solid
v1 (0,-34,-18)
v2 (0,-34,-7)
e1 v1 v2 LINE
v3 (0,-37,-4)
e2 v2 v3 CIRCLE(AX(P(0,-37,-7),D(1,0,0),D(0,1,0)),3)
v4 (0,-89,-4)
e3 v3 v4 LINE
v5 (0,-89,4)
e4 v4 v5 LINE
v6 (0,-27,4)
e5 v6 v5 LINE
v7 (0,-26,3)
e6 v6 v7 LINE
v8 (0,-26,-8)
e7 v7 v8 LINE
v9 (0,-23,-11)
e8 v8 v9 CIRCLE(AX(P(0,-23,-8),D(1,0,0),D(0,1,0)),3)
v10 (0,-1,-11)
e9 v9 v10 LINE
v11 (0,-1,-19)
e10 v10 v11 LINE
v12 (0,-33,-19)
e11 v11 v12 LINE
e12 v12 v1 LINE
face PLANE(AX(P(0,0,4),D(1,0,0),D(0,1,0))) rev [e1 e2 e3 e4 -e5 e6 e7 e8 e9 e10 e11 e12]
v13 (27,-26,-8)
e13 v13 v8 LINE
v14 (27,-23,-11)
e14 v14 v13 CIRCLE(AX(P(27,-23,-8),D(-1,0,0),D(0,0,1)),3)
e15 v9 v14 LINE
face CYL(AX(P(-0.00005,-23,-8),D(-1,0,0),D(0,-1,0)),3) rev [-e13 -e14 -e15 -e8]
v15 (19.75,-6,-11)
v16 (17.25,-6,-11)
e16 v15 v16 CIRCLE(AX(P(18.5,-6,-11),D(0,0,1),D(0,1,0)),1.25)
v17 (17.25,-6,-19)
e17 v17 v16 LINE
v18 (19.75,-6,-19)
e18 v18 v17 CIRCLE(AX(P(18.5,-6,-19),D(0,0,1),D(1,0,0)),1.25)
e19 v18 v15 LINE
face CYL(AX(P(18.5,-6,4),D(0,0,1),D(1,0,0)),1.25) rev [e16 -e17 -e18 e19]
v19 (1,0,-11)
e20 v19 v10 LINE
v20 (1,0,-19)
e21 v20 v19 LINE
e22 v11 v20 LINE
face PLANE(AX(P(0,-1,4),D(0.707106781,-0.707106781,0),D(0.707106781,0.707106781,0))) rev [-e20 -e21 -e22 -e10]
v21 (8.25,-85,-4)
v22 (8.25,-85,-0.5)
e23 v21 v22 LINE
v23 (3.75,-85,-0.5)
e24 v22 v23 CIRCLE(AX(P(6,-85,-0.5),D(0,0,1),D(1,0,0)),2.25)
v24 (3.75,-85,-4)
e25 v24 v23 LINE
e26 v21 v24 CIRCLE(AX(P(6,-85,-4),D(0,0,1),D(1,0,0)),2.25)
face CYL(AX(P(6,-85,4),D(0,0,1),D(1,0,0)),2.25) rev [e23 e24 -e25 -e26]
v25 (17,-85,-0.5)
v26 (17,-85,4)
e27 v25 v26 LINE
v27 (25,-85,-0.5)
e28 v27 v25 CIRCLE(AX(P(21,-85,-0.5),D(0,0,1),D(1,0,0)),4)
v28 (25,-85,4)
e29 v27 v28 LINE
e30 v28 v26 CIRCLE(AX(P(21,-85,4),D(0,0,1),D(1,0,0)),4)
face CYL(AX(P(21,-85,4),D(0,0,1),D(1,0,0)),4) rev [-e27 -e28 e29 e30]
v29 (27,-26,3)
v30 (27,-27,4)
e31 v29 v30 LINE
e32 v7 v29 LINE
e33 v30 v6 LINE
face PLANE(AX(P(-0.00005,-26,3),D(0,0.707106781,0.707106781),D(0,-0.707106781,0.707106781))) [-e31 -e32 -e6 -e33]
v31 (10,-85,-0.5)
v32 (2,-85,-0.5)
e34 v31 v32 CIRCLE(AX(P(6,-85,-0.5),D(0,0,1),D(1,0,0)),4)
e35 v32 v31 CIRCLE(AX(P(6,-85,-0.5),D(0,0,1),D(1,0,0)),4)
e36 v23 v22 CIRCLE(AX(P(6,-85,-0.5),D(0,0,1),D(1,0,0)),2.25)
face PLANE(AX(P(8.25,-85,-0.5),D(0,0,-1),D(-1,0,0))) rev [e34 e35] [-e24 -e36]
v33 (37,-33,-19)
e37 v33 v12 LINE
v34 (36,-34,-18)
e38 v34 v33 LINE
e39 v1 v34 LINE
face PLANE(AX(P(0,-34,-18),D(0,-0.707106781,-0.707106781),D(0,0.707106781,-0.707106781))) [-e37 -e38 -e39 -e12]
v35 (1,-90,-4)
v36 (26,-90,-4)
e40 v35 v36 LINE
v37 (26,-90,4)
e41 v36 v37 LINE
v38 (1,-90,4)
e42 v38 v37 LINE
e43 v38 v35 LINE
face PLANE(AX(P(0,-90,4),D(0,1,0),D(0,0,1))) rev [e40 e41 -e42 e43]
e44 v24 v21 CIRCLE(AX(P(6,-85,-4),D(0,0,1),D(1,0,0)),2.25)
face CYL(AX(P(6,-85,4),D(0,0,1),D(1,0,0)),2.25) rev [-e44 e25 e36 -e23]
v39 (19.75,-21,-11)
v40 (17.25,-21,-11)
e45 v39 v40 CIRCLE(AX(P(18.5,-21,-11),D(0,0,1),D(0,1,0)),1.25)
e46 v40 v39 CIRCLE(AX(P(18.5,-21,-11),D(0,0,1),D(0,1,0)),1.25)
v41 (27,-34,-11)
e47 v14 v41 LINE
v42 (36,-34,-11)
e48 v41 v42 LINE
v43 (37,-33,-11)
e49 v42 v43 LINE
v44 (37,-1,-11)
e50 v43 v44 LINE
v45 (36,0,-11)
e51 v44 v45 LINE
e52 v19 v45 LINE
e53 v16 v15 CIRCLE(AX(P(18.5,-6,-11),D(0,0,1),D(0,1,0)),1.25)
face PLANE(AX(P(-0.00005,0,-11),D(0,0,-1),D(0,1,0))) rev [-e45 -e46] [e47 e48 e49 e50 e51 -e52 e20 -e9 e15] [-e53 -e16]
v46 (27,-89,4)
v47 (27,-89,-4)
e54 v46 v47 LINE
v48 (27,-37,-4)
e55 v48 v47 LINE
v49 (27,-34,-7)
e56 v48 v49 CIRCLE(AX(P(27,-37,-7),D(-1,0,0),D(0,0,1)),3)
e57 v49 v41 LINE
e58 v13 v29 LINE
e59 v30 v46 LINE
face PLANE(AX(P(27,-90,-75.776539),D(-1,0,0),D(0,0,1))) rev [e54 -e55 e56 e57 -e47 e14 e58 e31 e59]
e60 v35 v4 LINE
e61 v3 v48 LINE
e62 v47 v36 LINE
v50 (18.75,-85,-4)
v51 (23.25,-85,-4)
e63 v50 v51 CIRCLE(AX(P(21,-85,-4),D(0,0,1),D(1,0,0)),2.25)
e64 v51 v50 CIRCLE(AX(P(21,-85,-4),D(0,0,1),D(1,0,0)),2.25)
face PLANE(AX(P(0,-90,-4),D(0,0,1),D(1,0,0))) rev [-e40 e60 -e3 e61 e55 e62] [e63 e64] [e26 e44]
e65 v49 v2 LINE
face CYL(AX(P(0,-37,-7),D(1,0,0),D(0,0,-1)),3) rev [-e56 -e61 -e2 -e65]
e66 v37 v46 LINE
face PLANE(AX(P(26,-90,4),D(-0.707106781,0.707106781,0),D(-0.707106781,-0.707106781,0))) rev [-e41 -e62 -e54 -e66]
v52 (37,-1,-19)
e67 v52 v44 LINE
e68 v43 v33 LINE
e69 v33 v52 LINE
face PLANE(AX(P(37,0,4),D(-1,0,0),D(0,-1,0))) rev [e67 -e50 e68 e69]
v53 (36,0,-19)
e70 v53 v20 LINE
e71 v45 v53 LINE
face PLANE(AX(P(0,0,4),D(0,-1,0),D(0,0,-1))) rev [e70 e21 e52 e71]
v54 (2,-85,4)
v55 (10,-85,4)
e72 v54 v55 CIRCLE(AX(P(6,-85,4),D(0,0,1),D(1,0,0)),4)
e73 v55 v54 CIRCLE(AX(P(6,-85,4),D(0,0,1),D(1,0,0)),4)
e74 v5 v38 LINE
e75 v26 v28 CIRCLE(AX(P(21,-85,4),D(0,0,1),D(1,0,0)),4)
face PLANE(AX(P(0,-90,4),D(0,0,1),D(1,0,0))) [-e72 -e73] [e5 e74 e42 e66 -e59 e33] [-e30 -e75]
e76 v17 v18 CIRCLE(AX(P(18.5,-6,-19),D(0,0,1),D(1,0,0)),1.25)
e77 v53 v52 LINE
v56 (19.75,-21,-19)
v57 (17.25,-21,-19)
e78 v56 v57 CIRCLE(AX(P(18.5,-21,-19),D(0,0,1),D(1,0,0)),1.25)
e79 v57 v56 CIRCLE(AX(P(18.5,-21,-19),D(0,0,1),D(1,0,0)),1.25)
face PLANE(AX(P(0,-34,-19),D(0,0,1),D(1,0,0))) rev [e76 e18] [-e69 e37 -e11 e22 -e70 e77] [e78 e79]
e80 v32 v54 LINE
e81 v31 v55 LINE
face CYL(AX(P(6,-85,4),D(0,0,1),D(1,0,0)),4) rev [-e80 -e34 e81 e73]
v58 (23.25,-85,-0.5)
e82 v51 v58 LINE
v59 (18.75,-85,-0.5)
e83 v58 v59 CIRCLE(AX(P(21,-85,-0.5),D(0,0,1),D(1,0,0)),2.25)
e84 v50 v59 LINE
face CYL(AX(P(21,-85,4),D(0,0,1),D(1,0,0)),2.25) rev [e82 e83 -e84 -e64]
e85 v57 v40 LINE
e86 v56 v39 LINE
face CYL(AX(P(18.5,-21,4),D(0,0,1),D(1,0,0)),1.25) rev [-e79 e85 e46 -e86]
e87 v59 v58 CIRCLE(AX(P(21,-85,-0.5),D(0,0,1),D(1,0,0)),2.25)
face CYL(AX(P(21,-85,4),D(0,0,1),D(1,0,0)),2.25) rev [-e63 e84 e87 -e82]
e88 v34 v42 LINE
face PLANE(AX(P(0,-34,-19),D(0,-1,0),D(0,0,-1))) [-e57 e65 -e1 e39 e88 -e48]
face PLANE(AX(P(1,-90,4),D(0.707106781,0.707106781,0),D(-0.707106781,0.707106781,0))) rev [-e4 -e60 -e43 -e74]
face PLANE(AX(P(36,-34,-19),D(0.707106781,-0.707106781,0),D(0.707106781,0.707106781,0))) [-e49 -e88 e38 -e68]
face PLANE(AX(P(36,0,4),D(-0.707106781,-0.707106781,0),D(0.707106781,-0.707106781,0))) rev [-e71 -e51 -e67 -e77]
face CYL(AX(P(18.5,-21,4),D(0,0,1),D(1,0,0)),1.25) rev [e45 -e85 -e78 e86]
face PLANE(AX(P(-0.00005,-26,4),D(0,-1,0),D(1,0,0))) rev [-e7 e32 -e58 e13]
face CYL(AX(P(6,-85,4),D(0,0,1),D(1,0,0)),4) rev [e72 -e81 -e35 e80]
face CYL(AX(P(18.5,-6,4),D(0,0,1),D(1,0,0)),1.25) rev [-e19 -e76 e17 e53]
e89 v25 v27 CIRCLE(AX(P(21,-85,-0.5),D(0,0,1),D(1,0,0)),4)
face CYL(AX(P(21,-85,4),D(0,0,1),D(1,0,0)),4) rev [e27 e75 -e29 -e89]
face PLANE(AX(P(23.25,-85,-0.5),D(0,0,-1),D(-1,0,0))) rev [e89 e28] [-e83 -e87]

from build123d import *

# Parameters (mm, degrees)
SKETCH1_W                               = 37
SKETCH1_H                               = 90
BOSS_EXTRUDE1_DEPTH                     = 4
SKETCH6_W                               = 37
SKETCH6_H                               = 34
BOSS_EXTRUDE2_DEPTH                     = 15
M3_TAPPED_HOLE1_D                       = 2.5
CBORE_FOR_M4_HEX_HEAD_BOLT1_D           = 4.5
CBORE_FOR_M4_HEX_HEAD_BOLT1_CBORE_D     = 8
CBORE_FOR_M4_HEX_HEAD_BOLT1_CBORE_DEPTH = 4.5
SKETCH7_W                               = 15
SKETCH7_H                               = 26
CUT_EXTRUDE1_DEPTH                      = 100.146356464
CUT_EXTRUDE2_REACH                      = 101.99
SKETCH8_W                               = 10
SKETCH8_H                               = 64
FILLET1_R                               = 3
CHAMFER1_SIZE                           = 1
CHAMFER2_SIZE                           = 1


with BuildPart() as part:
    # Sketch1 → Boss-Extrude1 (new, symmetric)
    with BuildSketch(Plane.XY):
        with Locations((18.5, -45)):
            Rectangle(SKETCH1_W, SKETCH1_H)
    extrude(amount=BOSS_EXTRUDE1_DEPTH, both=True)

    # Sketch6 → Boss-Extrude2 (add)
    with BuildSketch(Plane.XY.offset(-4)):
        with Locations((18.5, -17)):
            Rectangle(SKETCH6_W, SKETCH6_H)
    extrude(amount=-BOSS_EXTRUDE2_DEPTH)

    # M3 Tapped Hole1 (through all)
    with Locations(Plane.XY.offset(4)):
        with Locations((18.5, -21), (18.5, -6)):
            Hole(M3_TAPPED_HOLE1_D / 2)

    # CBORE for M4 Hex Head Bolt1 (through all)
    with Locations(Plane.XY.offset(4)):
        with Locations((6, -85), (21, -85)):
            CounterBoreHole(CBORE_FOR_M4_HEX_HEAD_BOLT1_D / 2, CBORE_FOR_M4_HEX_HEAD_BOLT1_CBORE_D / 2, CBORE_FOR_M4_HEX_HEAD_BOLT1_CBORE_DEPTH)

    # Sketch7 → Cut-Extrude1 (cut, through all)
    with BuildSketch(Plane(origin=(37, 0, 0), x_dir=(0, 0, -1), z_dir=(1, 0, 0))):
        with Locations((3.5, -13)):
            Rectangle(SKETCH7_W, SKETCH7_H)
    extrude(amount=-CUT_EXTRUDE1_DEPTH, mode=Mode.SUBTRACT)

    # Cut-Extrude2: up to this face of the body (flat: up to its plane)
    cut_extrude2_end = Plane(part.part.faces().sort_by_distance((18.5, -12.99484475, -11))[0])
    # Sketch8 → Cut-Extrude2 (cut, up to the picked face)
    with BuildSketch(Plane.XY.offset(4), mode=Mode.PRIVATE) as cut_extrude2_sk1:
        with Locations((32, -58)):
            Rectangle(SKETCH8_W, SKETCH8_H)
    cut_extrude2_tool1 = split(extrude(cut_extrude2_sk1.sketch, amount=-CUT_EXTRUDE2_REACH, mode=Mode.PRIVATE), bisect_by=cut_extrude2_end, keep=Keep.BOTH, mode=Mode.PRIVATE)
    add(cut_extrude2_tool1.solids().sort_by(Axis((32, -58, 4), (0, 0, -1)))[0], mode=Mode.SUBTRACT)

    # Fillet1
    fillet1_edges = [part.edges().sort_by_distance(p)[0] for p in [
        (13.5, -34, -4),
        (13.5, -26, -11),
    ]]
    fillet(fillet1_edges, radius=FILLET1_R)

    # Chamfer1
    chamfer1_edges = [part.edges().sort_by_distance(p)[0] for p in [
        (37, -34, -15),
        (37, 0, -15),
        (0, 0, -15),
        (0, -90, 0),
        (27, -90, 0),
    ]]
    chamfer(chamfer1_edges, length=CHAMFER1_SIZE)

    # Chamfer2
    chamfer2_edges = [part.edges().sort_by_distance(p)[0] for p in [
        (13.5, -26, 4),
        (18, -34, -19),
    ]]
    chamfer(chamfer2_edges, length=CHAMFER2_SIZE)


solid = part.part
